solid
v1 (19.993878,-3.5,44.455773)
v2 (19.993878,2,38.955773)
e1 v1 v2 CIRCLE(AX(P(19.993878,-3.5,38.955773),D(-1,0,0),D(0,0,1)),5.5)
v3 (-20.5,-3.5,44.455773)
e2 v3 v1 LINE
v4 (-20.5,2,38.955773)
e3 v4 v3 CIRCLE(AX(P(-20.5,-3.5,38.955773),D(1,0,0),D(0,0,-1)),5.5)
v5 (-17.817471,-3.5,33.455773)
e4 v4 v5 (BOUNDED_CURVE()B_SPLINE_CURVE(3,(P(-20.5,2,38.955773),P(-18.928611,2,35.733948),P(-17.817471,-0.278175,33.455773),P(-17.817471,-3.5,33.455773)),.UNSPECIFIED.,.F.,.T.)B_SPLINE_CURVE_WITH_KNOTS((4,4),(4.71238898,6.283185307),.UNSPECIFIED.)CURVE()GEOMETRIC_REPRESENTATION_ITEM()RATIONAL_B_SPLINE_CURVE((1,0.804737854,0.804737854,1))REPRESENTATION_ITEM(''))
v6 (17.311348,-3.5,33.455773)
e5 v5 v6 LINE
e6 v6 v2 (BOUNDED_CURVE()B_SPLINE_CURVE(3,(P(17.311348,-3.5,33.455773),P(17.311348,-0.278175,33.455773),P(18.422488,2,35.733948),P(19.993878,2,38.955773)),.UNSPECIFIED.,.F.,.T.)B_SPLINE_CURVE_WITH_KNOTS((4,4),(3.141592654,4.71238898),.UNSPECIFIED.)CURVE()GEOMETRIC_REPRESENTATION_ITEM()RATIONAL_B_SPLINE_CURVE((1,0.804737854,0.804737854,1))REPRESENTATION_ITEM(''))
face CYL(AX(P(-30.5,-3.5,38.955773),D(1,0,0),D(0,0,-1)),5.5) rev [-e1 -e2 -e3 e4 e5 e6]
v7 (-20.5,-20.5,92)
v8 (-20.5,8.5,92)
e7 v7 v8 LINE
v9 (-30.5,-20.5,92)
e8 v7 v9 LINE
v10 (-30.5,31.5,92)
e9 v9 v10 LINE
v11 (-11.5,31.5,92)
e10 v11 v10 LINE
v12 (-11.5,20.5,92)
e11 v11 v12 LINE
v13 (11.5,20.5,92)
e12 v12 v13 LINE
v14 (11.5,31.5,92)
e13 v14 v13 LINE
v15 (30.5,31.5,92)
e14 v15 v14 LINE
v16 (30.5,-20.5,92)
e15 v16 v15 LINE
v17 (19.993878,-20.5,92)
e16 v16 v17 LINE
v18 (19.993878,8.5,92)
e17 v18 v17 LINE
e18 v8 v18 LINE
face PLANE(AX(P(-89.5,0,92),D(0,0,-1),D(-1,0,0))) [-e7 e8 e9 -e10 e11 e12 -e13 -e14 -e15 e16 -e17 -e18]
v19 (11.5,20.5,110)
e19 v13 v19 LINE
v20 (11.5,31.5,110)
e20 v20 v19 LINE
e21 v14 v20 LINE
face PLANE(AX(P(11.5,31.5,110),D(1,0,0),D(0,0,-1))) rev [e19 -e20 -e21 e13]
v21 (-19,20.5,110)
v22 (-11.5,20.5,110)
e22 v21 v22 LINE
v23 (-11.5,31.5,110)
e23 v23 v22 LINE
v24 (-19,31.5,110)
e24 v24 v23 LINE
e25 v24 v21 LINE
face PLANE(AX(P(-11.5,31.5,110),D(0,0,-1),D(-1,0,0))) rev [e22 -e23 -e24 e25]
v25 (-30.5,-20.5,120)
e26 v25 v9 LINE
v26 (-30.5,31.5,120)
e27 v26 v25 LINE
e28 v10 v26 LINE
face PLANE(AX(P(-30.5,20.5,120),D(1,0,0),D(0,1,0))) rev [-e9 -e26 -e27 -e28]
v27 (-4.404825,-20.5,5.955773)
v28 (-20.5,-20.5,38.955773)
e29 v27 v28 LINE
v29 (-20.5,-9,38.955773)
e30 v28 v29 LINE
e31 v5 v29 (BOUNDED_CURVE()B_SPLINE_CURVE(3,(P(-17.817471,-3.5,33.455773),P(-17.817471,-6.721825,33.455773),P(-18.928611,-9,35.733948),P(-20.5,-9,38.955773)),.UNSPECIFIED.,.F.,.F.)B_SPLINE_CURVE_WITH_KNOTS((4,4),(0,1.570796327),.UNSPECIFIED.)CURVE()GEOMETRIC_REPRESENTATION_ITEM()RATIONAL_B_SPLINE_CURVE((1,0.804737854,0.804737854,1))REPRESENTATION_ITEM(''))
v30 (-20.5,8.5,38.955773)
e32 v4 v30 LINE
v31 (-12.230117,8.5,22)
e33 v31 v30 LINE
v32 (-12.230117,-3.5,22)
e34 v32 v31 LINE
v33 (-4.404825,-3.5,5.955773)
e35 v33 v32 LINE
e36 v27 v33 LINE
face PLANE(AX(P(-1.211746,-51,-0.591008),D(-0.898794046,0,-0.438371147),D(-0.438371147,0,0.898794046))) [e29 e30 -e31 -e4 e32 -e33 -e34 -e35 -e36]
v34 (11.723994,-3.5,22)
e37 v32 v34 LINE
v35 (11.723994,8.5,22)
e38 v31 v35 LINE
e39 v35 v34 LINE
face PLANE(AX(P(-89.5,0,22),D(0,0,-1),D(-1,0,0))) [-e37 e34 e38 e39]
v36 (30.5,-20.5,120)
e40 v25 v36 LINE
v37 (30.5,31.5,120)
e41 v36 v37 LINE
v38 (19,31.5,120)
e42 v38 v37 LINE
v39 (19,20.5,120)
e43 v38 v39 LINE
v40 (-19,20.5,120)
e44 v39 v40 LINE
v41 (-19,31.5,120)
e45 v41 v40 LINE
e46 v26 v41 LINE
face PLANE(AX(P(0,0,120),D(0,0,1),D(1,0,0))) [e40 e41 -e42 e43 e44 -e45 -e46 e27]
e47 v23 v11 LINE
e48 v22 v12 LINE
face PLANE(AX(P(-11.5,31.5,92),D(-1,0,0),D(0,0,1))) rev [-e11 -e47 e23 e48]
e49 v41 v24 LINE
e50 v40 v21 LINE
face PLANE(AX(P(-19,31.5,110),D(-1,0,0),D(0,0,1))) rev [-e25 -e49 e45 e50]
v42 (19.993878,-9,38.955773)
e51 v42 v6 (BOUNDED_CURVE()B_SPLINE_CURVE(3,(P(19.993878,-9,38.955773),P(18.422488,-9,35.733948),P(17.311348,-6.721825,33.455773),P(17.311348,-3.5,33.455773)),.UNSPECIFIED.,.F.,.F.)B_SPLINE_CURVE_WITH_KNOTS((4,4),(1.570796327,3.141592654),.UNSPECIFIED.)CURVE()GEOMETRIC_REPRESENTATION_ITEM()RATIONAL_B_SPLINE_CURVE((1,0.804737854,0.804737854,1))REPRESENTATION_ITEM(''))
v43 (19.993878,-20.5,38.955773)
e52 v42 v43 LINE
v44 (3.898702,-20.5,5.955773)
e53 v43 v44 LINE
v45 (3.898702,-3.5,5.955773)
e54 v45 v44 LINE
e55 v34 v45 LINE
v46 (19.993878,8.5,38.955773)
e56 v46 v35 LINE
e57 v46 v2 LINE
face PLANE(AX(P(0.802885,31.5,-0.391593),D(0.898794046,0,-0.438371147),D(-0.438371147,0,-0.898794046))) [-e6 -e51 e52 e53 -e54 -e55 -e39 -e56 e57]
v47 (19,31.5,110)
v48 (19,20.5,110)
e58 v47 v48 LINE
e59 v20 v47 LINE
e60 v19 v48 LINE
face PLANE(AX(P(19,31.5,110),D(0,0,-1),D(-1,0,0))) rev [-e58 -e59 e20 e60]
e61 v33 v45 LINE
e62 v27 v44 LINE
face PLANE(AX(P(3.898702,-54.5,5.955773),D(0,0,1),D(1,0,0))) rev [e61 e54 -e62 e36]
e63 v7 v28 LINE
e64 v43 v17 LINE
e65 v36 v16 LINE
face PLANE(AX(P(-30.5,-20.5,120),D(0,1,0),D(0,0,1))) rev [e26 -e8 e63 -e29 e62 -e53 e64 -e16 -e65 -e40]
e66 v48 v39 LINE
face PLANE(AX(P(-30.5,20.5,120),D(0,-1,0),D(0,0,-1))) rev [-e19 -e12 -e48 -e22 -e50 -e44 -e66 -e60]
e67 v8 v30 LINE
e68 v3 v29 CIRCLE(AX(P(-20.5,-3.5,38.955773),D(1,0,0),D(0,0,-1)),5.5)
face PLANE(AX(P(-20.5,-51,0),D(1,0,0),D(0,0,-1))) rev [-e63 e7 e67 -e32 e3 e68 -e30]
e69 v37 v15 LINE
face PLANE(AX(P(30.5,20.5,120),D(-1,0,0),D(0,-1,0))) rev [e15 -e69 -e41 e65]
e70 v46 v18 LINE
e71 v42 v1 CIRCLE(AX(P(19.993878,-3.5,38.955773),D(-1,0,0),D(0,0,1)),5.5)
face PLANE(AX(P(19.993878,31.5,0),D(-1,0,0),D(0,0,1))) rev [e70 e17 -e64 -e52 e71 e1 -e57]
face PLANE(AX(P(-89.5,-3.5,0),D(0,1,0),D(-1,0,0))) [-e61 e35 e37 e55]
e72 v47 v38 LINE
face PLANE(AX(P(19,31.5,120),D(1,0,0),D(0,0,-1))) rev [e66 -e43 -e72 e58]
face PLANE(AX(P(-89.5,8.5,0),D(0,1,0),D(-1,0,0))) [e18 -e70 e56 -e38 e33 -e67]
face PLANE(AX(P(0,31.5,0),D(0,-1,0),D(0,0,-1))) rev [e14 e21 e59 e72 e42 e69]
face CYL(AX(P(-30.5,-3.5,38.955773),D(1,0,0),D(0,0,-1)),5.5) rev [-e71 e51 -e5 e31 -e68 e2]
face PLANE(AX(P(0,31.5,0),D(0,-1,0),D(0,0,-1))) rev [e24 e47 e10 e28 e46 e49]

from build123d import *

# Parameters (mm, degrees)
BASE_BLOCK_PROFILE_W         = 61
BASE_BLOCK_PROFILE_H         = 41
BASE_BLOCK_41X61X120_DEPTH   = 120
LENGTHWISE_STEP_CUT_DEPTH    = 120
CASTELLATED_END_BOSSES_DEPTH = 11
TAPERED_NOSE_CUT_DEPTH       = 128.759539761
TAPERED_NOSE_CUT_DEPTH_BACK  = 51
TAPERED_NOSE_PROFILE_W       = 10
TAPERED_NOSE_PROFILE_H       = 86.04422701
TAPERED_NOSE_PROFILE_W_2     = 10.506122453
NOSE_SLOT_CUT_DEPTH          = 51
CROSS_HOLE_DEPTH             = 128.759539761
CROSS_HOLE_DEPTH_BACK        = 128.759539761
CROSS_HOLE_PROFILE_R         = 5.5


with BuildPart() as part:
    # Base Block Profile → Base Block 41x61x120 (new body)
    with BuildSketch(Plane.XY):
        Rectangle(BASE_BLOCK_PROFILE_W, BASE_BLOCK_PROFILE_H)
    extrude(amount=BASE_BLOCK_41X61X120_DEPTH)

    # Step Cut Profile → Lengthwise Step Cut (cut)
    with BuildSketch(Plane(origin=(30.5, 0, 0), x_dir=(0, 0, -1), z_dir=(1, 0, 0))):
        Polygon((-22, -3.5), (0, -3.5), (0, 20.5), (-92, 20.5), (-92, 8.5), (-22, 8.5), align=None)
    extrude(amount=-LENGTHWISE_STEP_CUT_DEPTH, mode=Mode.SUBTRACT)

    # End Boss Profile → Castellated End Bosses (add)
    with BuildSketch(Plane(origin=(0, 20.5, 0), x_dir=(1, 0, 0), z_dir=(0, 1, 0))):
        Polygon((-19, -120), (-30.5, -120), (-30.5, -92), (-11.5, -92), (-11.5, -110), (-19, -110), align=None)
        Polygon((11.5, -92), (30.5, -92), (30.5, -120), (19, -120), (19, -110), (11.5, -110), align=None)
    extrude(amount=CASTELLATED_END_BOSSES_DEPTH)

    # Tapered Nose Profile → Tapered Nose Cut (cut, two sides: drawn at the far end of the back side and taken through both)
    with BuildSketch(Plane(origin=(0, 0, 0), x_dir=(1, 0, 0), z_dir=(0, 1, 0)).offset(-TAPERED_NOSE_CUT_DEPTH_BACK)):
        with Locations((-25.5, -48.977886495)):
            Rectangle(TAPERED_NOSE_PROFILE_W, TAPERED_NOSE_PROFILE_H)
        with Locations((25.246938774, -48.977886495)):
            Rectangle(TAPERED_NOSE_PROFILE_W_2, TAPERED_NOSE_PROFILE_H)
        Polygon((19.993877547, -5.95577299), (3.898702125, -5.95577299), (19.993877547, -38.95577299), align=None)
        Polygon((-20.5, -38.95577299), (-4.404824577, -5.95577299), (-20.5, -5.95577299), align=None)
    extrude(amount=TAPERED_NOSE_CUT_DEPTH + TAPERED_NOSE_CUT_DEPTH_BACK, mode=Mode.SUBTRACT)

    # Nose Slot Profile → Nose Slot Cut (cut)
    with BuildSketch(Plane(origin=(0, -3.5, 0), x_dir=(1, 0, 0), z_dir=(0, 1, 0))):
        Polygon((-30.5, -5.95577299), (3.898702125, -5.95577299), (30.5, -5.95577299), (30.5, 0), (-30.5, 0), align=None)
    extrude(amount=-NOSE_SLOT_CUT_DEPTH, mode=Mode.SUBTRACT)

    # Cross Hole Profile → Cross Hole (cut, two sides: drawn at the far end of the back side and taken through both)
    with BuildSketch(Plane(origin=(0, 0, 0), x_dir=(0, 0, -1), z_dir=(1, 0, 0)).offset(-CROSS_HOLE_DEPTH_BACK)):
        with Locations(Location((-38.95577299, -3.5, 0), (0, 0, 90))):
            Circle(CROSS_HOLE_PROFILE_R)
    extrude(amount=CROSS_HOLE_DEPTH + CROSS_HOLE_DEPTH_BACK, mode=Mode.SUBTRACT)


solid = part.part
